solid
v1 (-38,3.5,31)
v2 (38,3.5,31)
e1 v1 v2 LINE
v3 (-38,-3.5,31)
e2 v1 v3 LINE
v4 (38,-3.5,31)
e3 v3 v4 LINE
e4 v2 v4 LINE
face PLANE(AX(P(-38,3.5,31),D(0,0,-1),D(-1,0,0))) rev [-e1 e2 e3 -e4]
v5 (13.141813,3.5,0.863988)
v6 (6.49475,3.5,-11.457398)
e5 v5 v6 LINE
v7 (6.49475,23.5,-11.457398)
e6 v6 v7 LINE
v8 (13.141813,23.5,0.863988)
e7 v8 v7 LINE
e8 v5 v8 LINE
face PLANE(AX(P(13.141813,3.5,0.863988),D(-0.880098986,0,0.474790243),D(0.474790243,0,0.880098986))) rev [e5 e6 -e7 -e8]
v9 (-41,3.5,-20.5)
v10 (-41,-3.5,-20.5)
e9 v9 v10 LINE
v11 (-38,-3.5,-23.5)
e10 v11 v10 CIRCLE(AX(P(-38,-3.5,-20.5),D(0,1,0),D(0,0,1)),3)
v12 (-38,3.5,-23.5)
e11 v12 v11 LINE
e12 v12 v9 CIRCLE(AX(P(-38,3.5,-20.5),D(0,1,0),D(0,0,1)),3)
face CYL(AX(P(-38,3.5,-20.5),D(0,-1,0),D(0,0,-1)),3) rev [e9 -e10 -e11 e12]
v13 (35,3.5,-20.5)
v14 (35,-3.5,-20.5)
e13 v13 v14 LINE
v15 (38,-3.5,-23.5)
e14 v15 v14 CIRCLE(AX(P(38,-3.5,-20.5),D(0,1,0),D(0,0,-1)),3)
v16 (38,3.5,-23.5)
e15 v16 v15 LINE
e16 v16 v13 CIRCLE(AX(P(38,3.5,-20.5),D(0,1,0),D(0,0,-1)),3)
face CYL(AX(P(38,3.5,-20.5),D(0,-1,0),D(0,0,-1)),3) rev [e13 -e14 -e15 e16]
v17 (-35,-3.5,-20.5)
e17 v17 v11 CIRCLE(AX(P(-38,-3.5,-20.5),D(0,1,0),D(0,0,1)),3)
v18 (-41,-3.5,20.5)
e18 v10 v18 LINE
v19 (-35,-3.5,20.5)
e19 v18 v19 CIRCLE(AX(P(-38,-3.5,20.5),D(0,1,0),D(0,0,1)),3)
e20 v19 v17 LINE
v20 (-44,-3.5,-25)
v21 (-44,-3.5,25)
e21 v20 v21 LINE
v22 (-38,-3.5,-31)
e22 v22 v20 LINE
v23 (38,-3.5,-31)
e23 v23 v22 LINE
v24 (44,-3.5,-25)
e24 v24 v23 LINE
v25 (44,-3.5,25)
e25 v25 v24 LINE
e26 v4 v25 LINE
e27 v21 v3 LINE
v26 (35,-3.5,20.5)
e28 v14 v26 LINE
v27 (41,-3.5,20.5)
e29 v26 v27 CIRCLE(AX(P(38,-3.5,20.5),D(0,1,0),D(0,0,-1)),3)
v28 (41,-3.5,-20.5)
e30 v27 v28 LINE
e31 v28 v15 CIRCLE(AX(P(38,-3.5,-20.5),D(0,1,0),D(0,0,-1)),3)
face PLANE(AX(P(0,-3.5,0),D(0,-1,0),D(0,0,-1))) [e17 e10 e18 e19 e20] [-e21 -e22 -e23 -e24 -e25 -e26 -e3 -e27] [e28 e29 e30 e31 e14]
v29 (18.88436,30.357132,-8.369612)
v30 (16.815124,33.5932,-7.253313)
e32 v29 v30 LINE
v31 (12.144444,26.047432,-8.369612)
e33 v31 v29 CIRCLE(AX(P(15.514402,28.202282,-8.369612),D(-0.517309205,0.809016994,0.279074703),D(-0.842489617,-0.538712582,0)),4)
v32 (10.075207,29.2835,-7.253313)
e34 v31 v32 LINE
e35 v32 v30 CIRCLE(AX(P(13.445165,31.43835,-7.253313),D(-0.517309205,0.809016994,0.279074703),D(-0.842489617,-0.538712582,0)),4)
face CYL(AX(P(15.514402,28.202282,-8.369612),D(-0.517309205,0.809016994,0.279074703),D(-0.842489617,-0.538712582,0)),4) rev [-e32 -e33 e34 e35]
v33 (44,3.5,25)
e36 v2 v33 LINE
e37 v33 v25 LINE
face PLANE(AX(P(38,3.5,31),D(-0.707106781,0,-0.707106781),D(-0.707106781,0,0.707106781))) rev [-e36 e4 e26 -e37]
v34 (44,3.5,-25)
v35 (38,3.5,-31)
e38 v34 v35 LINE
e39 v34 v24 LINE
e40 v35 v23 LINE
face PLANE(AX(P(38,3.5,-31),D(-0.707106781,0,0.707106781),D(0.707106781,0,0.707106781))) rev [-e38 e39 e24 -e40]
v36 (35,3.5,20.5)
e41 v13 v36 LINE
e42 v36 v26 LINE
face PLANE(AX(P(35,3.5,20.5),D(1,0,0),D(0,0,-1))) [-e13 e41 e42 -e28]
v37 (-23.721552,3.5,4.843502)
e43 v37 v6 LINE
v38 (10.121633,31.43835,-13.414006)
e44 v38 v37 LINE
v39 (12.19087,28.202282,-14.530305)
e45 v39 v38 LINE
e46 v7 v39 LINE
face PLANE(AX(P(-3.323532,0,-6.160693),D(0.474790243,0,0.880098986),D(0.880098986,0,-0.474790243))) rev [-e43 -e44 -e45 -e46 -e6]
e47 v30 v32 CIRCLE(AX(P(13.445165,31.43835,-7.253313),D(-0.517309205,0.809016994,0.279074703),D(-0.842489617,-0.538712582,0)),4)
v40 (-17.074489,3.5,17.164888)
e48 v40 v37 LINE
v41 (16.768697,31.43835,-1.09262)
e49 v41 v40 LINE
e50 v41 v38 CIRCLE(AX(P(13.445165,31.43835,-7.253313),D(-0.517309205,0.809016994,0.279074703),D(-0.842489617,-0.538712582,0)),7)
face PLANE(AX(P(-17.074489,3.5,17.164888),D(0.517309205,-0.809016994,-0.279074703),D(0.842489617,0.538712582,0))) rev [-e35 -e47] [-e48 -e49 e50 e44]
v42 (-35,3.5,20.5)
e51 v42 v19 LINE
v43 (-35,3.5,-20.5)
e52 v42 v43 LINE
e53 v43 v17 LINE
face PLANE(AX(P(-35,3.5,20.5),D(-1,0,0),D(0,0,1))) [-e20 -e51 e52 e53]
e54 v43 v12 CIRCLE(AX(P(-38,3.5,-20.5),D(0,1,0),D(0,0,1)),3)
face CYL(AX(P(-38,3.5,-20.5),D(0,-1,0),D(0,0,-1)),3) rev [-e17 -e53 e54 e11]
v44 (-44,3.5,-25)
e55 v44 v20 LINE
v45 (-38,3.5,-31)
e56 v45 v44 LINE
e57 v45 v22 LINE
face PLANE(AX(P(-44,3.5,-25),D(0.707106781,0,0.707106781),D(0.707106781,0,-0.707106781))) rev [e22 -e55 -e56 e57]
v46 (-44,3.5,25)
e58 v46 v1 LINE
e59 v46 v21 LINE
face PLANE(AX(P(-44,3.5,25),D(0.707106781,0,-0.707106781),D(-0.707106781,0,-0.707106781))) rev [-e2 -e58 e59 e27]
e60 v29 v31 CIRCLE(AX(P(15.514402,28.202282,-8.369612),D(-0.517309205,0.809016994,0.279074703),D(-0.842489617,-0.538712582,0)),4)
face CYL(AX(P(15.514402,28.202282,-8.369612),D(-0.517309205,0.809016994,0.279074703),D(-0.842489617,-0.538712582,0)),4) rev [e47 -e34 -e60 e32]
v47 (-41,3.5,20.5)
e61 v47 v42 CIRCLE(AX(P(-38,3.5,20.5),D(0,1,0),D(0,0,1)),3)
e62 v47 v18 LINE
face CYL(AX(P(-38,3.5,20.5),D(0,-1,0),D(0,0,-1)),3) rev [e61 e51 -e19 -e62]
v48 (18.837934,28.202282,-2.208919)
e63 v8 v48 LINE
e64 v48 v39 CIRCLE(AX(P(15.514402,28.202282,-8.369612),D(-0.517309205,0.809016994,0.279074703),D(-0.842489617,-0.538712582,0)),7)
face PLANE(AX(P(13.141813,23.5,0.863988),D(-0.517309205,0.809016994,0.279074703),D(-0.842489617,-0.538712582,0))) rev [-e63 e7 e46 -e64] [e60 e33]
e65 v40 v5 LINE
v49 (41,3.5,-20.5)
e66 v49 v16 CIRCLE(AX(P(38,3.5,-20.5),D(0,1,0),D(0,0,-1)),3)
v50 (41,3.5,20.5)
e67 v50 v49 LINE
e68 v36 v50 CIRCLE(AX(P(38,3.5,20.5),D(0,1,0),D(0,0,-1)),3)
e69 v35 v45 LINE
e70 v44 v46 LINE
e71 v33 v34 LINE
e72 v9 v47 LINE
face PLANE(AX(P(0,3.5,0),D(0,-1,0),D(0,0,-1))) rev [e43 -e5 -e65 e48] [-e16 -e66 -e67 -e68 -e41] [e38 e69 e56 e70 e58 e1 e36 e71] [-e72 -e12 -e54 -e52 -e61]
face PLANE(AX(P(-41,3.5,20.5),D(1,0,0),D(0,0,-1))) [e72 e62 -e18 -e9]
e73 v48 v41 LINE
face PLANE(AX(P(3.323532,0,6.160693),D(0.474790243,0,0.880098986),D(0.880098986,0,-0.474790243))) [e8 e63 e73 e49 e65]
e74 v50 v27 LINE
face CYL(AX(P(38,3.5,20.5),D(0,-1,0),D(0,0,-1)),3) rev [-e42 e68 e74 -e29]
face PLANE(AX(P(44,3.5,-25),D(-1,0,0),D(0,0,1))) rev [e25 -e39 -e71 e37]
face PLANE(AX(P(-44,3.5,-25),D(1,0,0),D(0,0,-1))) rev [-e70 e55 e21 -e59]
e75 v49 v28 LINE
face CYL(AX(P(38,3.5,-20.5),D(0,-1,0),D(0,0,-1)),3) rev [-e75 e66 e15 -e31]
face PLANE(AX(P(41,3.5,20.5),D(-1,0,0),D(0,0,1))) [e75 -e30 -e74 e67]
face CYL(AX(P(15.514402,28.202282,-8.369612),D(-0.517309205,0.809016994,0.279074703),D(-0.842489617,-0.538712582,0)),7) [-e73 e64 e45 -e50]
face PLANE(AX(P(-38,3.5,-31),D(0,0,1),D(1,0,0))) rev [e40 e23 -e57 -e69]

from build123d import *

# Parameters (mm, degrees)
BASE_PLATE_88X62X7_DEPTH = 3.5
LIFTING_LUG_DEPTH        = 7
LUG_EYE_BOSS_SKETCH_R    = 7
LUG_EYE_BOSS_DEPTH       = 4
EYE_HOLE_SKETCH_R        = 4
EYE_HOLE_8_DEPTH         = 4


with BuildPart() as part:
    # Base Plate Sketch → Base Plate 88x62x7 (new, symmetric)
    with BuildSketch(Plane(origin=(0, 0, 0), x_dir=(1, 0, 0), z_dir=(0, 1, 0))):
        Polygon((-44, 25), (-38, 31), (38, 31), (44, 25), (44, -25), (38, -31), (-38, -31), (-44, -25), align=None)
        with BuildLine():
            Line((-41, -20.5), (-41, 20.5))
            ThreePointArc((-41, 20.5), (-38, 23.5), (-35, 20.5))
            Line((-35, 20.5), (-35, -20.5))
            ThreePointArc((-35, -20.5), (-38, -23.5), (-41, -20.5))
        make_face(mode=Mode.SUBTRACT)
        with BuildLine():
            Line((41, -20.5), (41, 20.5))
            ThreePointArc((41, 20.5), (38, 23.5), (35, 20.5))
            Line((35, 20.5), (35, -20.5))
            ThreePointArc((35, -20.5), (38, -23.5), (41, -20.5))
        make_face(mode=Mode.SUBTRACT)
    extrude(amount=BASE_PLATE_88X62X7_DEPTH, both=True)

    # Lug Profile Sketch → Lifting Lug (add, symmetric)
    with BuildSketch(Plane(origin=(0, 0, 0), x_dir=(0.8800989862281835, 0, -0.47479024257046787), z_dir=(0.47479024257046787, 0, 0.8800989862281835))):
        Polygon((-23.176961449, 3.5), (15.276878373, 31.438349996), (17.628019382, 28.202282018), (11.155883427, 23.5), (11.155883427, 3.5), align=None)
    extrude(amount=LIFTING_LUG_DEPTH, both=True)

    # Lug Eye Boss Sketch → Lug Eye Boss (add)
    with BuildSketch(Plane(origin=(-8.512134462, 13.312079847, 4.592072539), x_dir=(0.8557985667033265, 0.4890308937191984, 0.16869380017278038), z_dir=(-0.5173092046624842, 0.8090169943749463, 0.27907470251528765))):
        with Locations((25.657088578, 17.108817488)):
            Circle(LUG_EYE_BOSS_SKETCH_R)
    extrude(amount=-LUG_EYE_BOSS_DEPTH)

    # Eye Hole Sketch → Eye Hole Ø8 (cut)
    with BuildSketch(Plane(origin=(-8.512134462, 13.312079847, 4.592072539), x_dir=(0.8557985667033265, 0.4890308937191984, 0.16869380017278038), z_dir=(-0.5173092046624842, 0.8090169943749463, 0.27907470251528765))):
        with Locations(Location((25.657088578, 17.108817488, 0), (0, 0, 190.117848847))):
            Circle(EYE_HOLE_SKETCH_R)
    extrude(amount=-EYE_HOLE_8_DEPTH, mode=Mode.SUBTRACT)


solid = part.part
